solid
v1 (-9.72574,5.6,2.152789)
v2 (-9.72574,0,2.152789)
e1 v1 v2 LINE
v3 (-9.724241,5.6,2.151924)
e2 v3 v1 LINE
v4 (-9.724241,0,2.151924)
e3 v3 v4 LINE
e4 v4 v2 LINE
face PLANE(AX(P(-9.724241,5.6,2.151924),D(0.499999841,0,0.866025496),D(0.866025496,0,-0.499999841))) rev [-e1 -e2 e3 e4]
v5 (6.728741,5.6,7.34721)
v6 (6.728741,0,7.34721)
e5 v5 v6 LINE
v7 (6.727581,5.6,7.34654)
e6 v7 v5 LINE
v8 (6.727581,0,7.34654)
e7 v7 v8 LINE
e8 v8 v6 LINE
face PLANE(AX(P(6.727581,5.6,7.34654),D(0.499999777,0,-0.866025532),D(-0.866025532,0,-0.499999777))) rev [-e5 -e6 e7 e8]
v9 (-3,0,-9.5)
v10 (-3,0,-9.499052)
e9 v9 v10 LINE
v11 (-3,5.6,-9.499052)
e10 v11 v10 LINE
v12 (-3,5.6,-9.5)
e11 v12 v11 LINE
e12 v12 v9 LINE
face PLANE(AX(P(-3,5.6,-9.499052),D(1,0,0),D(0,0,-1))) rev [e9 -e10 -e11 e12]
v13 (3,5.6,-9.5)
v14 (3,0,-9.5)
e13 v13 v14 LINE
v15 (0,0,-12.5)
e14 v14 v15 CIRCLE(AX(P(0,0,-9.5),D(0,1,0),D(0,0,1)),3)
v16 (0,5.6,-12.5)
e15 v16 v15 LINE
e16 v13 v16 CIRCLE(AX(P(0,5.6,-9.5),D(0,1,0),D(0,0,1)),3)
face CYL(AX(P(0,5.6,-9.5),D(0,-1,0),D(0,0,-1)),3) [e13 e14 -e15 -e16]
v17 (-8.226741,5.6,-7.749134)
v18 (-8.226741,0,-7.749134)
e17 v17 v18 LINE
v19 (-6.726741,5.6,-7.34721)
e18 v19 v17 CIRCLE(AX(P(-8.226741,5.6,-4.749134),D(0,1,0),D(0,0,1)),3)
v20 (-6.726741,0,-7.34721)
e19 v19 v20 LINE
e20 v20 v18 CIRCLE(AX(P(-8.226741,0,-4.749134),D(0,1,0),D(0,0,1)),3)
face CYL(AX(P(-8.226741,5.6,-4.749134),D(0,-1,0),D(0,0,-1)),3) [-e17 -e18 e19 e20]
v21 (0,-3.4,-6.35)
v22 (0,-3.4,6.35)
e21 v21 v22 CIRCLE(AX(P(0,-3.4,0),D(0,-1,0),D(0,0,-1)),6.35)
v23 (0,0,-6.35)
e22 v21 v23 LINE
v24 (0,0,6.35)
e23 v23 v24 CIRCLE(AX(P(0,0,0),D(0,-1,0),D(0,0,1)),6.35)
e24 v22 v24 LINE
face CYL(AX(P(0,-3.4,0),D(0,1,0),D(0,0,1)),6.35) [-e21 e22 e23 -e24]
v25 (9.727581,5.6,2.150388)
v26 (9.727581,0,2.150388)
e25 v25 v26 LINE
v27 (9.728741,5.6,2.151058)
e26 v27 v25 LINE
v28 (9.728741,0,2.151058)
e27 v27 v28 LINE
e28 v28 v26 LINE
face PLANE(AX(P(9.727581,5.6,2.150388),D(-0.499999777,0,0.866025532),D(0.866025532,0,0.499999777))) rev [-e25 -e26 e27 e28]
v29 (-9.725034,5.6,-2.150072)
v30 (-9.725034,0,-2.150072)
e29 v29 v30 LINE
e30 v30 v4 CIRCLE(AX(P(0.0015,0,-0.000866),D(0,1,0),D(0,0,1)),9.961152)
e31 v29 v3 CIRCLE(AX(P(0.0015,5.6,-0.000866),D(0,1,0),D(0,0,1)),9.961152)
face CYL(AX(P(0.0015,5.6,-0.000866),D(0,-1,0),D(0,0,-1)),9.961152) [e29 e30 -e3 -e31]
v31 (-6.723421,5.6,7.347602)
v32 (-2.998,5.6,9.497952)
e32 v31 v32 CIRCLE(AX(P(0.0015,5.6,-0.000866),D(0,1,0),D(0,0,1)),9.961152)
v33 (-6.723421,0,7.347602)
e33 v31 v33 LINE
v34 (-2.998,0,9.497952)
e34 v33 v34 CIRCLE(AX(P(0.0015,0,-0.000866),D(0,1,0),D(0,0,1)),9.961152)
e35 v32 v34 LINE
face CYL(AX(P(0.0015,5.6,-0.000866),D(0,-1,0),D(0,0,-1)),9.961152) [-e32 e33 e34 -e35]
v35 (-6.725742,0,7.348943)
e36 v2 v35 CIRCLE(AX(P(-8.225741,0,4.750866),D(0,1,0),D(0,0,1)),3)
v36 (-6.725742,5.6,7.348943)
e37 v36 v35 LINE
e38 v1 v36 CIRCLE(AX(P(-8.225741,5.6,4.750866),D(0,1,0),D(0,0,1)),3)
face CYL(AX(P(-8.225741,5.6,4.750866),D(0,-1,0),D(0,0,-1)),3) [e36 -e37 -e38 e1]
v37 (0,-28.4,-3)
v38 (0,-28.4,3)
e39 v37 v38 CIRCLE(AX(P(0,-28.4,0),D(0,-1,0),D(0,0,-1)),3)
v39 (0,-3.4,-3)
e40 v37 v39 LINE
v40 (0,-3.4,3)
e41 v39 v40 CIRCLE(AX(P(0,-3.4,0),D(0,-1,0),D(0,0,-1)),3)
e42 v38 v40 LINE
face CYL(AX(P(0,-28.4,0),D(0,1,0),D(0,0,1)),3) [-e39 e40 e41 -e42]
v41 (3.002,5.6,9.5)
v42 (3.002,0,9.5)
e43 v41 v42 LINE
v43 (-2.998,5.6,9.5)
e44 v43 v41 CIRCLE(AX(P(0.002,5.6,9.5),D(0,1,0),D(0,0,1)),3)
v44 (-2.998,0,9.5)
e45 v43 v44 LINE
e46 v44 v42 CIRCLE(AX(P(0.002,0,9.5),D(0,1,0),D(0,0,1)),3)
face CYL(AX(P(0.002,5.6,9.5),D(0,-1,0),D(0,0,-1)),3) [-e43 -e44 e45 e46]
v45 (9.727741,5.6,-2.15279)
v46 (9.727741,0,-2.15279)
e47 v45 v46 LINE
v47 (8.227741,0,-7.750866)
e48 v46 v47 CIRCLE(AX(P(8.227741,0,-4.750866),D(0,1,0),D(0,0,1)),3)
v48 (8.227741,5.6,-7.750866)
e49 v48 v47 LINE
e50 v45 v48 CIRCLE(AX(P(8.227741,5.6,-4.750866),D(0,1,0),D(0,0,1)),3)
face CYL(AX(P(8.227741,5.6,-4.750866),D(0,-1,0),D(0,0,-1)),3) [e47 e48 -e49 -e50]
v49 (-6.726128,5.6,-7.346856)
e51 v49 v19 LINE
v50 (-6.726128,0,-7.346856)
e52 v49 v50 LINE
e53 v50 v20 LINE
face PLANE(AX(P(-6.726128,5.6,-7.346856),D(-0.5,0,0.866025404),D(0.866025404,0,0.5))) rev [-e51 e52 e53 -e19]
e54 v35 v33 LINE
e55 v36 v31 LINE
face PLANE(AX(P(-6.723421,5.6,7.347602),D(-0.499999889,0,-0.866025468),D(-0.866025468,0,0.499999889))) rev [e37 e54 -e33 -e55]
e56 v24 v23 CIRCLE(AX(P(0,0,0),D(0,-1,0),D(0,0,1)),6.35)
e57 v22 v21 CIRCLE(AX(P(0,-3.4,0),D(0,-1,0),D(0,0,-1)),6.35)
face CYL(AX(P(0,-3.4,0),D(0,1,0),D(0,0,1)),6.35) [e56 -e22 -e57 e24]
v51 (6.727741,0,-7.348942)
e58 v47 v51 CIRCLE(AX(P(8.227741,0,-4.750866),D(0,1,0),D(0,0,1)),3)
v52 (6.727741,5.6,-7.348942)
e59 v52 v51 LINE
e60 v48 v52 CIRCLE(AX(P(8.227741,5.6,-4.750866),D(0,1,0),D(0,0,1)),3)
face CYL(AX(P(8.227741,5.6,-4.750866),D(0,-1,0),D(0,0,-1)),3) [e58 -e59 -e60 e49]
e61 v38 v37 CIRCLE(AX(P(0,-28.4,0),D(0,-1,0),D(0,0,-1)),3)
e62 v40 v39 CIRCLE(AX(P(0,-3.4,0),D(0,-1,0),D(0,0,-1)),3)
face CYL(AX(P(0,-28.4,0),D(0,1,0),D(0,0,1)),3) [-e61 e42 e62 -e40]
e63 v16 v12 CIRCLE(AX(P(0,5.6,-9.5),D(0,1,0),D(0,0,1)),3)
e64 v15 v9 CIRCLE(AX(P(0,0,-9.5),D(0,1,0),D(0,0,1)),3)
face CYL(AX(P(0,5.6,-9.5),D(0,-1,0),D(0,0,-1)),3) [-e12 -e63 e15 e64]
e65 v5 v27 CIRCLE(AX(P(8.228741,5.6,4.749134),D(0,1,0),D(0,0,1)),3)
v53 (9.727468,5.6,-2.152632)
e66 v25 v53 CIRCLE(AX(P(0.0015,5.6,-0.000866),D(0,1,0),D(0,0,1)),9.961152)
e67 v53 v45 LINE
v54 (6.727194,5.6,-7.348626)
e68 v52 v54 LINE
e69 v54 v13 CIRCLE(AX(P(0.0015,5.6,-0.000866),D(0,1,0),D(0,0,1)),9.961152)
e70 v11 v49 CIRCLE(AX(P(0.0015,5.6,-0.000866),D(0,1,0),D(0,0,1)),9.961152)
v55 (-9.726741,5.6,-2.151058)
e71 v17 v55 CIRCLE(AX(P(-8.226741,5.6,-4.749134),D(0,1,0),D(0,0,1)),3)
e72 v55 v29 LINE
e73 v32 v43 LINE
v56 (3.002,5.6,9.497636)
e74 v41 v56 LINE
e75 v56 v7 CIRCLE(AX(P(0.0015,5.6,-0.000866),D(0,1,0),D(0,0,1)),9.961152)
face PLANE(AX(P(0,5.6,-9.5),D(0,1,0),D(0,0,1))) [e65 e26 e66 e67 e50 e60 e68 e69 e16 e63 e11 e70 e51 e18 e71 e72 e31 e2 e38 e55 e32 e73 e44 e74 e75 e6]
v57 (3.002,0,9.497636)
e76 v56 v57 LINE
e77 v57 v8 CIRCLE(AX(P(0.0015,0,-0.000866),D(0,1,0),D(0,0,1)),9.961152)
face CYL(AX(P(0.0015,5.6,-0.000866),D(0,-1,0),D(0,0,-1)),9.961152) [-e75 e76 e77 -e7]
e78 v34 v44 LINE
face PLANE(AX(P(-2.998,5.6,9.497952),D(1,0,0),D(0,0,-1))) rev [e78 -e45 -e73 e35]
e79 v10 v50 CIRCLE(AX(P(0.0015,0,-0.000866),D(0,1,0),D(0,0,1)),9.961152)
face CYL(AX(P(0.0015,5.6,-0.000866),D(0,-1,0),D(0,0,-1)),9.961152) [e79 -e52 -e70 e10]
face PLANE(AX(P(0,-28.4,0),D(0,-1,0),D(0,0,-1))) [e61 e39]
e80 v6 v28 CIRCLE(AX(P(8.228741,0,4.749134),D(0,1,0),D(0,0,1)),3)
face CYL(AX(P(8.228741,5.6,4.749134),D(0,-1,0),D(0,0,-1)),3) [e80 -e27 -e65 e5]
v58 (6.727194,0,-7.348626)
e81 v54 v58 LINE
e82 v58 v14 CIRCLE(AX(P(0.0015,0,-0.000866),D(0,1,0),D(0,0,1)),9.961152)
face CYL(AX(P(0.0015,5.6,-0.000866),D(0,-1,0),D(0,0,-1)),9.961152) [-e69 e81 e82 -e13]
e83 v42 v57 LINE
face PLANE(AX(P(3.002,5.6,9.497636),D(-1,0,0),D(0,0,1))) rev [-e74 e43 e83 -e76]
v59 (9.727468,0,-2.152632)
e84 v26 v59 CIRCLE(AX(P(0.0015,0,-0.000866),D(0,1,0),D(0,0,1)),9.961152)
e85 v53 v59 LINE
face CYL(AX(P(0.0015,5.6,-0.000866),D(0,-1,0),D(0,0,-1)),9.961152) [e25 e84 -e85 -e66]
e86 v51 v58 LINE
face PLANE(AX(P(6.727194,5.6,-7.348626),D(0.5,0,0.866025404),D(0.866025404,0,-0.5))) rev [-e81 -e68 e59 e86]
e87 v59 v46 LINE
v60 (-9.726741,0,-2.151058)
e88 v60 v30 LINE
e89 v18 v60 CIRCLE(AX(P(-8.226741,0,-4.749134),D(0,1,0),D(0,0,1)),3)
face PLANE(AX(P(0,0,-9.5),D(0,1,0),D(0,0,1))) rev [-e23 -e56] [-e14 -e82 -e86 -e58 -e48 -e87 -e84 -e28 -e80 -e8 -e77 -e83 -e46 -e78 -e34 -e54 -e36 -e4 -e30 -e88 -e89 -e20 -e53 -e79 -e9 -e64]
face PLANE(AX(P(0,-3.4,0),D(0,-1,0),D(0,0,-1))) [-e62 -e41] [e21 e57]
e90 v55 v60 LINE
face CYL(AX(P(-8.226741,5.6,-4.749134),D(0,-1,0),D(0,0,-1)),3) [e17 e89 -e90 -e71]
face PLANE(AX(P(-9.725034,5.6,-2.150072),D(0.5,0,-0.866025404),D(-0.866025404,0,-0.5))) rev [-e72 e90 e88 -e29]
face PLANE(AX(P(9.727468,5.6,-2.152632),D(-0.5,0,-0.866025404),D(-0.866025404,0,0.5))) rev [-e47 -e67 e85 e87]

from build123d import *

# Parameters (mm, degrees)
BOSS_EXTRUDE1_DEPTH = 5.6
SKETCH2_R           = 6.35
BOSS_EXTRUDE2_DEPTH = 3.4
SKETCH3_R           = 3
BOSS_EXTRUDE3_DEPTH = 25


with BuildPart() as part:
    # Sketch1 → Boss-Extrude1 (new body)
    with BuildSketch(Plane(origin=(0, 0, 0), x_dir=(1, 0, 0), z_dir=(0, 1, 0))):
        with BuildLine():
            Line((-9.72424134, -2.15192377), (-9.725740285, -2.152789186))
            ThreePointArc((-9.725740285, -2.152789186), (-10.823817926, -6.250865027), (-6.725742085, -7.348942669))
            Line((-6.725742085, -7.348942669), (-6.723420775, -7.34760246))
            ThreePointArc((-6.723420775, -7.34760246), (-4.978167749, -8.626268935), (-2.998, -9.497952231))
            Line((-2.998, -9.497952231), (-2.998, -9.5))
            ThreePointArc((-2.998, -9.5), (0.002000003, -12.499999996), (3.002, -9.499999993))
            Line((3.002, -9.499999993), (3.002, -9.497636397))
            ThreePointArc((3.002, -9.497636397), (4.982303032, -8.625613539), (6.727581168, -7.346540363))
            Line((6.727581168, -7.346540363), (6.728741336, -7.347210186))
            ThreePointArc((6.728741336, -7.347210186), (10.826817547, -6.249133975), (9.728741336, -2.151057763))
            Line((9.728741336, -2.151057763), (9.727581168, -2.15038794))
            ThreePointArc((9.727581168, -2.15038794), (9.962651964, 0.001128196), (9.727467916, 2.152631955))
            ThreePointArc((9.727467916, 2.152631955), (10.825817547, 6.250866025), (6.727194396, 7.348626461))
            ThreePointArc((6.727194396, 7.348626461), (4.981167779, 8.628000969), (3, 9.5))
            ThreePointArc((3, 9.5), (2e-09, 12.5), (-3, 9.499052498))
            ThreePointArc((-3, 9.499052498), (-4.980665222, 8.626558938), (-6.726128008, 7.346856081))
            ThreePointArc((-6.726128008, 7.346856081), (-10.824817547, 6.249133975), (-9.726741336, 2.151057764))
            Line((-9.726741336, 2.151057764), (-9.725033927, 2.150071991))
            ThreePointArc((-9.725033927, 2.150071991), (-9.959651798, -0.000969188), (-9.72424134, -2.15192377))
        make_face()
    extrude(amount=BOSS_EXTRUDE1_DEPTH)

    # Sketch2 → Boss-Extrude2 (add)
    with BuildSketch(Plane.XZ):
        with Locations(Location((0, 0, 0), (0, 0, 90))):
            Circle(SKETCH2_R)
    extrude(amount=BOSS_EXTRUDE2_DEPTH)

    # Sketch3 → Boss-Extrude3 (add)
    with BuildSketch(Plane.XZ.offset(3.4)):
        with Locations(Location((0, 0, 0), (0, 0, 270))):
            Circle(SKETCH3_R)
    extrude(amount=BOSS_EXTRUDE3_DEPTH)


solid = part.part
